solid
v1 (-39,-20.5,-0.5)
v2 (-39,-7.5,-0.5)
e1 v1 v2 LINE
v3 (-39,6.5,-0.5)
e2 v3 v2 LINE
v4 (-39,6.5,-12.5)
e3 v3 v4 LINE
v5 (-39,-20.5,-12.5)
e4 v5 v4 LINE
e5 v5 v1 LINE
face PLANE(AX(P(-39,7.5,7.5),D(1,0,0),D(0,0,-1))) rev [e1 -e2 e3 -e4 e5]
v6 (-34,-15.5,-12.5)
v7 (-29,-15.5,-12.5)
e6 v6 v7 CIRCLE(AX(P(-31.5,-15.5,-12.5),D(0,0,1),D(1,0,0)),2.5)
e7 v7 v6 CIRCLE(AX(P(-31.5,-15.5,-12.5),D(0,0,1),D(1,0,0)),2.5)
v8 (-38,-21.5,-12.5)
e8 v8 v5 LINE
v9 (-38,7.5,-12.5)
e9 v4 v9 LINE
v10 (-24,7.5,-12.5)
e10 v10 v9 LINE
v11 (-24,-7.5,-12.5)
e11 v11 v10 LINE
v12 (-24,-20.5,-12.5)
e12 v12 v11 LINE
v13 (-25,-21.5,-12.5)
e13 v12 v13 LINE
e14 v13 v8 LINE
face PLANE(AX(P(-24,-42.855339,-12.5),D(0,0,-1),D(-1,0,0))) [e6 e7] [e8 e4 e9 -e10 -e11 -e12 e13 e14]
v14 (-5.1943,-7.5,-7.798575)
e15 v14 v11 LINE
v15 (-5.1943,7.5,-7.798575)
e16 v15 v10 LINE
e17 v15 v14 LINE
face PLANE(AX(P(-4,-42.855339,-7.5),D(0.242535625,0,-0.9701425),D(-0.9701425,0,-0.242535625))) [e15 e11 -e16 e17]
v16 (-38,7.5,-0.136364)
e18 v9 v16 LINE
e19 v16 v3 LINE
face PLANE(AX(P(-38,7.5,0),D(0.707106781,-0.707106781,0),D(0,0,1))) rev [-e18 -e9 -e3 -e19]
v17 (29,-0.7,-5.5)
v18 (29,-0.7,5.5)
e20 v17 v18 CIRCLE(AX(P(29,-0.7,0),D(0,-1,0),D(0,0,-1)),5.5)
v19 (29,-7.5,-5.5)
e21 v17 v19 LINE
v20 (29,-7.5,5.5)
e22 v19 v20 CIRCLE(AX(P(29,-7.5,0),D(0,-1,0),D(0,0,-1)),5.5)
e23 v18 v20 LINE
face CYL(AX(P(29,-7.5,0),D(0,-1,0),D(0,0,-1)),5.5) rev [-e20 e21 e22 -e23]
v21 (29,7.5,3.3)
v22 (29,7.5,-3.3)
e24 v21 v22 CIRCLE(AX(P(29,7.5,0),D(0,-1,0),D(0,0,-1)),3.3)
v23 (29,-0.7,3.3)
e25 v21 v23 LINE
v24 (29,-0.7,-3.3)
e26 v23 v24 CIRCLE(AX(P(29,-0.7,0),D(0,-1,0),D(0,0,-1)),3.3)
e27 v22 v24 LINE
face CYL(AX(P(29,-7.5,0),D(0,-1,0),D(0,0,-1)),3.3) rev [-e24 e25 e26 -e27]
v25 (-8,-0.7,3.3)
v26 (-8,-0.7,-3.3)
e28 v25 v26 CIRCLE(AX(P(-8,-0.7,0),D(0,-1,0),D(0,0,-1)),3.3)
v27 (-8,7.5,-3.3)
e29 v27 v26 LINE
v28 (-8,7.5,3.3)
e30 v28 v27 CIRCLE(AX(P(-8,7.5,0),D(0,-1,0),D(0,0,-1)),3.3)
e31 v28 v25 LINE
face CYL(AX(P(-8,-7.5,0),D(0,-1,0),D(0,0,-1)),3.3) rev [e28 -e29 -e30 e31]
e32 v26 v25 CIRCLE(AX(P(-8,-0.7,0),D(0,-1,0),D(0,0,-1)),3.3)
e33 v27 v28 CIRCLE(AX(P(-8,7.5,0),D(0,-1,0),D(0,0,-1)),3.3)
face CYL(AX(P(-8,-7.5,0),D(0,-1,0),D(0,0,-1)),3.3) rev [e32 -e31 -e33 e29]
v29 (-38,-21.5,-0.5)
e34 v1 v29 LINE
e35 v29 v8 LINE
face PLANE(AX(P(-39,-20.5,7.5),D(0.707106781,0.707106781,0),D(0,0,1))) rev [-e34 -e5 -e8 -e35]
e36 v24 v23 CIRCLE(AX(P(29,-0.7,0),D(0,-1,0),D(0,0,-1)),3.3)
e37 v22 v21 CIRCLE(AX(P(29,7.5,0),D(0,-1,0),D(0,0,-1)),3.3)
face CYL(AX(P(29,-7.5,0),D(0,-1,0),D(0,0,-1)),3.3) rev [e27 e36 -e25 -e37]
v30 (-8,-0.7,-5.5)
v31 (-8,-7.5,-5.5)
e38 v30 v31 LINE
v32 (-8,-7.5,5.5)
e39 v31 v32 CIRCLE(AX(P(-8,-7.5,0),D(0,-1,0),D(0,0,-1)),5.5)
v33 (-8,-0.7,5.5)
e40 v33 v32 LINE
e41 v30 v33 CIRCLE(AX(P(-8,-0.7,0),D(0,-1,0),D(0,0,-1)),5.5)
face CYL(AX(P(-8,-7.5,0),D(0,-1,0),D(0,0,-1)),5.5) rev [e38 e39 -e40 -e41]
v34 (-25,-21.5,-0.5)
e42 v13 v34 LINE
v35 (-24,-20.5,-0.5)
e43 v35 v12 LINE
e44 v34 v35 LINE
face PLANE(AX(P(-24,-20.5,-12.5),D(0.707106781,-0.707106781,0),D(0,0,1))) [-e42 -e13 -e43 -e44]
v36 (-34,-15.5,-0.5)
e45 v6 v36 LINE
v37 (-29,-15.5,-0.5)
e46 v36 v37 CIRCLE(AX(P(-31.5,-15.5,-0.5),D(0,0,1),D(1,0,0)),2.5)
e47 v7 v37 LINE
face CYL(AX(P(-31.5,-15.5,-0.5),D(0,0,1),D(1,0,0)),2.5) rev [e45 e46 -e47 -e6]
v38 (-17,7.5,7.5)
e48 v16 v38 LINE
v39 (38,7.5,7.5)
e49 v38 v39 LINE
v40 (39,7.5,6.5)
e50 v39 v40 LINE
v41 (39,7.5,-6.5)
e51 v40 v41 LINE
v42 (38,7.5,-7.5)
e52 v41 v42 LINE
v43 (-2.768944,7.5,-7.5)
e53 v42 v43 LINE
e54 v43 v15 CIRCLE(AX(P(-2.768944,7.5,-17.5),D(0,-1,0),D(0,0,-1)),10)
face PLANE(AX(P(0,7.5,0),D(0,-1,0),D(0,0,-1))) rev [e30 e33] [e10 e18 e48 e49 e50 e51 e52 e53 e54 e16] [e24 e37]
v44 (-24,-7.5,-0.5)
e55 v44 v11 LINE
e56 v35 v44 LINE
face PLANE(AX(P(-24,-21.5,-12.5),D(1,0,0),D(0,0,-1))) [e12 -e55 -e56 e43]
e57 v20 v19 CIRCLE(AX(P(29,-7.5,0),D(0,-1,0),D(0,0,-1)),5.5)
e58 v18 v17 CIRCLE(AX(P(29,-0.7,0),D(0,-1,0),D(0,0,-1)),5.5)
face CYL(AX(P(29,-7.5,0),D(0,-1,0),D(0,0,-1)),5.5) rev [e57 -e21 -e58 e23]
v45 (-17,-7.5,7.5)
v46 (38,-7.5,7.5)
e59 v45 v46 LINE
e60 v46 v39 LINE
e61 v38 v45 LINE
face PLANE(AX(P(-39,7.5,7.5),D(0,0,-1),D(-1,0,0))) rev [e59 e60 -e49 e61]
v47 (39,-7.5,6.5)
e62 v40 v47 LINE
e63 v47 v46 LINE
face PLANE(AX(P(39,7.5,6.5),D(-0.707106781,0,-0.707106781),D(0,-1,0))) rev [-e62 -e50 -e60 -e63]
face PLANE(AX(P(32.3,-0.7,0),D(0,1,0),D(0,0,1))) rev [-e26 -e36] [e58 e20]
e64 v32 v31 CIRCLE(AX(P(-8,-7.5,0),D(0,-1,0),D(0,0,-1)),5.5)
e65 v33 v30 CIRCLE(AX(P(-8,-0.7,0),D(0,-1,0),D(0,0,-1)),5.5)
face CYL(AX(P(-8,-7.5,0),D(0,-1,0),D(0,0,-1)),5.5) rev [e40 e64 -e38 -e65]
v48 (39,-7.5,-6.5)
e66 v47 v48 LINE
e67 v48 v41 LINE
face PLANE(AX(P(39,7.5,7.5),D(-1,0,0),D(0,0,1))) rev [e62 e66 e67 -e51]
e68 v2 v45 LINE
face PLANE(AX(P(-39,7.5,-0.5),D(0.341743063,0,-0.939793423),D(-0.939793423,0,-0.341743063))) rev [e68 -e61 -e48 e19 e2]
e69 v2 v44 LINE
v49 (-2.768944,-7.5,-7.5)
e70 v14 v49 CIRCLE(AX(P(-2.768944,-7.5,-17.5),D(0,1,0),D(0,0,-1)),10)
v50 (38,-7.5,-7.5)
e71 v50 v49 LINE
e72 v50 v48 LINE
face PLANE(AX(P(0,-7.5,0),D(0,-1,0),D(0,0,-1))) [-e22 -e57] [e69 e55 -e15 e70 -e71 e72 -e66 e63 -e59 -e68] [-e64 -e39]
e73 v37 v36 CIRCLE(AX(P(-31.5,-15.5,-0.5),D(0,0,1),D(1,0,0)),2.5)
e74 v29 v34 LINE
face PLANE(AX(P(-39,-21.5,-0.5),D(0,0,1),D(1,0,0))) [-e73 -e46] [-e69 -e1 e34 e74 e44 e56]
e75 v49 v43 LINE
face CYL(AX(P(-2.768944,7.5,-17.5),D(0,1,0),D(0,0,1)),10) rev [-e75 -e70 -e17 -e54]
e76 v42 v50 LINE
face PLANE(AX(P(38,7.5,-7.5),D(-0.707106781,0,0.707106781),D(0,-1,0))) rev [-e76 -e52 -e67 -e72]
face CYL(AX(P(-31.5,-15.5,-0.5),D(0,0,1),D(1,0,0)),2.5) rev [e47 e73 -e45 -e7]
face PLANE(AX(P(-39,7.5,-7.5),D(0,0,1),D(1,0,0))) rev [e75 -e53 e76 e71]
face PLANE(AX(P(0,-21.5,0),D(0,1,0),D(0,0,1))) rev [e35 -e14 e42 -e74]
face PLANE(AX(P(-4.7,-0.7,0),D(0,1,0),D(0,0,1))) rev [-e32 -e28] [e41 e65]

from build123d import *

# Parameters (mm, degrees)
SKETCH_1_W                   = 78
SKETCH_1_H                   = 15
EXTRUDE_1_DEPTH              = 7.5
HOLE_WIZARD_M6_1_D           = 6.6
HOLE_WIZARD_M6_1_CBORE_D     = 11
HOLE_WIZARD_M6_1_CBORE_DEPTH = 6.8
EXTRUDE_3_DEPTH              = 15
SKETCH_2_W                   = 15
SKETCH_2_H                   = 12
EXTRUDE_2_DEPTH              = 14
HOLE_WIZARD_M6_1_2_D         = 5
CUT_EXTRUDE_1_DEPTH          = 51.182168148
CHAMFER_1_SIZE               = 1
FILLET_2_R                   = 10


with BuildPart() as part:
    # 草图1 → 凸台-拉伸1 (new, symmetric)
    with BuildSketch(Plane(origin=(0, 0, 0), x_dir=(1, 0, 0), z_dir=(0, 1, 0))):
        Rectangle(SKETCH_1_W, SKETCH_1_H)
    extrude(amount=EXTRUDE_1_DEPTH, both=True)

    # Hole Wizard M6 _1 (through all)
    with Locations(Plane.XZ.offset(7.5)):
        with Locations((29, 0), (-8, 0)):
            CounterBoreHole(HOLE_WIZARD_M6_1_D / 2, HOLE_WIZARD_M6_1_CBORE_D / 2, HOLE_WIZARD_M6_1_CBORE_DEPTH)

    # 草图8 → 凸台-拉伸3 (add)
    with BuildSketch(Plane(origin=(0, 7.5, 0), x_dir=(1, 0, 0), z_dir=(0, 1, 0))):
        Polygon((-24, 12.5), (-39, 12.5), (-39, 7.5), (-4, 7.5), align=None)
    extrude(amount=-EXTRUDE_3_DEPTH)

    # 草图2 → 凸台-拉伸2 (add)
    with BuildSketch(Plane(origin=(0, -7.5, 0), x_dir=(1, 0, 0), z_dir=(0, 1, 0))):
        with Locations((-31.5, 6.5)):
            Rectangle(SKETCH_2_W, SKETCH_2_H)
    extrude(amount=-EXTRUDE_2_DEPTH)

    # Hole Wizard M6 _1 2 (through all)
    with Locations(Plane(origin=(-28.5, 0, -0.5), x_dir=(1, 0, 0), z_dir=(0, 0, 1))):
        with Locations((-3, -15.5)):
            Hole(HOLE_WIZARD_M6_1_2_D / 2)

    # 草图9 → 切除-拉伸1 (cut, through all)
    with BuildSketch(Plane(origin=(0, -21.5, 0), x_dir=(-1, 0, 0), z_dir=(0, -1, 0))):
        Polygon((39, 0.5), (39, -7.5), (17, -7.5), align=None)
    extrude(amount=-CUT_EXTRUDE_1_DEPTH, mode=Mode.SUBTRACT)

    # 倒角1
    chamfer_1_edges = [part.edges().sort_by_distance(p)[0] for p in [
        (-39, 7.5, -6.5),
        (-39, -21.5, -6.5),
        (-24, -21.5, -6.5),
        (39, 0, 7.5),
        (39, 0, -7.5),
    ]]
    chamfer(chamfer_1_edges, length=CHAMFER_1_SIZE)

    # 圆角2
    fillet_2_edges = [part.edges().sort_by_distance(p)[0] for p in [
        (-4, 0, -7.5),
    ]]
    fillet(fillet_2_edges, radius=FILLET_2_R)


solid = part.part
